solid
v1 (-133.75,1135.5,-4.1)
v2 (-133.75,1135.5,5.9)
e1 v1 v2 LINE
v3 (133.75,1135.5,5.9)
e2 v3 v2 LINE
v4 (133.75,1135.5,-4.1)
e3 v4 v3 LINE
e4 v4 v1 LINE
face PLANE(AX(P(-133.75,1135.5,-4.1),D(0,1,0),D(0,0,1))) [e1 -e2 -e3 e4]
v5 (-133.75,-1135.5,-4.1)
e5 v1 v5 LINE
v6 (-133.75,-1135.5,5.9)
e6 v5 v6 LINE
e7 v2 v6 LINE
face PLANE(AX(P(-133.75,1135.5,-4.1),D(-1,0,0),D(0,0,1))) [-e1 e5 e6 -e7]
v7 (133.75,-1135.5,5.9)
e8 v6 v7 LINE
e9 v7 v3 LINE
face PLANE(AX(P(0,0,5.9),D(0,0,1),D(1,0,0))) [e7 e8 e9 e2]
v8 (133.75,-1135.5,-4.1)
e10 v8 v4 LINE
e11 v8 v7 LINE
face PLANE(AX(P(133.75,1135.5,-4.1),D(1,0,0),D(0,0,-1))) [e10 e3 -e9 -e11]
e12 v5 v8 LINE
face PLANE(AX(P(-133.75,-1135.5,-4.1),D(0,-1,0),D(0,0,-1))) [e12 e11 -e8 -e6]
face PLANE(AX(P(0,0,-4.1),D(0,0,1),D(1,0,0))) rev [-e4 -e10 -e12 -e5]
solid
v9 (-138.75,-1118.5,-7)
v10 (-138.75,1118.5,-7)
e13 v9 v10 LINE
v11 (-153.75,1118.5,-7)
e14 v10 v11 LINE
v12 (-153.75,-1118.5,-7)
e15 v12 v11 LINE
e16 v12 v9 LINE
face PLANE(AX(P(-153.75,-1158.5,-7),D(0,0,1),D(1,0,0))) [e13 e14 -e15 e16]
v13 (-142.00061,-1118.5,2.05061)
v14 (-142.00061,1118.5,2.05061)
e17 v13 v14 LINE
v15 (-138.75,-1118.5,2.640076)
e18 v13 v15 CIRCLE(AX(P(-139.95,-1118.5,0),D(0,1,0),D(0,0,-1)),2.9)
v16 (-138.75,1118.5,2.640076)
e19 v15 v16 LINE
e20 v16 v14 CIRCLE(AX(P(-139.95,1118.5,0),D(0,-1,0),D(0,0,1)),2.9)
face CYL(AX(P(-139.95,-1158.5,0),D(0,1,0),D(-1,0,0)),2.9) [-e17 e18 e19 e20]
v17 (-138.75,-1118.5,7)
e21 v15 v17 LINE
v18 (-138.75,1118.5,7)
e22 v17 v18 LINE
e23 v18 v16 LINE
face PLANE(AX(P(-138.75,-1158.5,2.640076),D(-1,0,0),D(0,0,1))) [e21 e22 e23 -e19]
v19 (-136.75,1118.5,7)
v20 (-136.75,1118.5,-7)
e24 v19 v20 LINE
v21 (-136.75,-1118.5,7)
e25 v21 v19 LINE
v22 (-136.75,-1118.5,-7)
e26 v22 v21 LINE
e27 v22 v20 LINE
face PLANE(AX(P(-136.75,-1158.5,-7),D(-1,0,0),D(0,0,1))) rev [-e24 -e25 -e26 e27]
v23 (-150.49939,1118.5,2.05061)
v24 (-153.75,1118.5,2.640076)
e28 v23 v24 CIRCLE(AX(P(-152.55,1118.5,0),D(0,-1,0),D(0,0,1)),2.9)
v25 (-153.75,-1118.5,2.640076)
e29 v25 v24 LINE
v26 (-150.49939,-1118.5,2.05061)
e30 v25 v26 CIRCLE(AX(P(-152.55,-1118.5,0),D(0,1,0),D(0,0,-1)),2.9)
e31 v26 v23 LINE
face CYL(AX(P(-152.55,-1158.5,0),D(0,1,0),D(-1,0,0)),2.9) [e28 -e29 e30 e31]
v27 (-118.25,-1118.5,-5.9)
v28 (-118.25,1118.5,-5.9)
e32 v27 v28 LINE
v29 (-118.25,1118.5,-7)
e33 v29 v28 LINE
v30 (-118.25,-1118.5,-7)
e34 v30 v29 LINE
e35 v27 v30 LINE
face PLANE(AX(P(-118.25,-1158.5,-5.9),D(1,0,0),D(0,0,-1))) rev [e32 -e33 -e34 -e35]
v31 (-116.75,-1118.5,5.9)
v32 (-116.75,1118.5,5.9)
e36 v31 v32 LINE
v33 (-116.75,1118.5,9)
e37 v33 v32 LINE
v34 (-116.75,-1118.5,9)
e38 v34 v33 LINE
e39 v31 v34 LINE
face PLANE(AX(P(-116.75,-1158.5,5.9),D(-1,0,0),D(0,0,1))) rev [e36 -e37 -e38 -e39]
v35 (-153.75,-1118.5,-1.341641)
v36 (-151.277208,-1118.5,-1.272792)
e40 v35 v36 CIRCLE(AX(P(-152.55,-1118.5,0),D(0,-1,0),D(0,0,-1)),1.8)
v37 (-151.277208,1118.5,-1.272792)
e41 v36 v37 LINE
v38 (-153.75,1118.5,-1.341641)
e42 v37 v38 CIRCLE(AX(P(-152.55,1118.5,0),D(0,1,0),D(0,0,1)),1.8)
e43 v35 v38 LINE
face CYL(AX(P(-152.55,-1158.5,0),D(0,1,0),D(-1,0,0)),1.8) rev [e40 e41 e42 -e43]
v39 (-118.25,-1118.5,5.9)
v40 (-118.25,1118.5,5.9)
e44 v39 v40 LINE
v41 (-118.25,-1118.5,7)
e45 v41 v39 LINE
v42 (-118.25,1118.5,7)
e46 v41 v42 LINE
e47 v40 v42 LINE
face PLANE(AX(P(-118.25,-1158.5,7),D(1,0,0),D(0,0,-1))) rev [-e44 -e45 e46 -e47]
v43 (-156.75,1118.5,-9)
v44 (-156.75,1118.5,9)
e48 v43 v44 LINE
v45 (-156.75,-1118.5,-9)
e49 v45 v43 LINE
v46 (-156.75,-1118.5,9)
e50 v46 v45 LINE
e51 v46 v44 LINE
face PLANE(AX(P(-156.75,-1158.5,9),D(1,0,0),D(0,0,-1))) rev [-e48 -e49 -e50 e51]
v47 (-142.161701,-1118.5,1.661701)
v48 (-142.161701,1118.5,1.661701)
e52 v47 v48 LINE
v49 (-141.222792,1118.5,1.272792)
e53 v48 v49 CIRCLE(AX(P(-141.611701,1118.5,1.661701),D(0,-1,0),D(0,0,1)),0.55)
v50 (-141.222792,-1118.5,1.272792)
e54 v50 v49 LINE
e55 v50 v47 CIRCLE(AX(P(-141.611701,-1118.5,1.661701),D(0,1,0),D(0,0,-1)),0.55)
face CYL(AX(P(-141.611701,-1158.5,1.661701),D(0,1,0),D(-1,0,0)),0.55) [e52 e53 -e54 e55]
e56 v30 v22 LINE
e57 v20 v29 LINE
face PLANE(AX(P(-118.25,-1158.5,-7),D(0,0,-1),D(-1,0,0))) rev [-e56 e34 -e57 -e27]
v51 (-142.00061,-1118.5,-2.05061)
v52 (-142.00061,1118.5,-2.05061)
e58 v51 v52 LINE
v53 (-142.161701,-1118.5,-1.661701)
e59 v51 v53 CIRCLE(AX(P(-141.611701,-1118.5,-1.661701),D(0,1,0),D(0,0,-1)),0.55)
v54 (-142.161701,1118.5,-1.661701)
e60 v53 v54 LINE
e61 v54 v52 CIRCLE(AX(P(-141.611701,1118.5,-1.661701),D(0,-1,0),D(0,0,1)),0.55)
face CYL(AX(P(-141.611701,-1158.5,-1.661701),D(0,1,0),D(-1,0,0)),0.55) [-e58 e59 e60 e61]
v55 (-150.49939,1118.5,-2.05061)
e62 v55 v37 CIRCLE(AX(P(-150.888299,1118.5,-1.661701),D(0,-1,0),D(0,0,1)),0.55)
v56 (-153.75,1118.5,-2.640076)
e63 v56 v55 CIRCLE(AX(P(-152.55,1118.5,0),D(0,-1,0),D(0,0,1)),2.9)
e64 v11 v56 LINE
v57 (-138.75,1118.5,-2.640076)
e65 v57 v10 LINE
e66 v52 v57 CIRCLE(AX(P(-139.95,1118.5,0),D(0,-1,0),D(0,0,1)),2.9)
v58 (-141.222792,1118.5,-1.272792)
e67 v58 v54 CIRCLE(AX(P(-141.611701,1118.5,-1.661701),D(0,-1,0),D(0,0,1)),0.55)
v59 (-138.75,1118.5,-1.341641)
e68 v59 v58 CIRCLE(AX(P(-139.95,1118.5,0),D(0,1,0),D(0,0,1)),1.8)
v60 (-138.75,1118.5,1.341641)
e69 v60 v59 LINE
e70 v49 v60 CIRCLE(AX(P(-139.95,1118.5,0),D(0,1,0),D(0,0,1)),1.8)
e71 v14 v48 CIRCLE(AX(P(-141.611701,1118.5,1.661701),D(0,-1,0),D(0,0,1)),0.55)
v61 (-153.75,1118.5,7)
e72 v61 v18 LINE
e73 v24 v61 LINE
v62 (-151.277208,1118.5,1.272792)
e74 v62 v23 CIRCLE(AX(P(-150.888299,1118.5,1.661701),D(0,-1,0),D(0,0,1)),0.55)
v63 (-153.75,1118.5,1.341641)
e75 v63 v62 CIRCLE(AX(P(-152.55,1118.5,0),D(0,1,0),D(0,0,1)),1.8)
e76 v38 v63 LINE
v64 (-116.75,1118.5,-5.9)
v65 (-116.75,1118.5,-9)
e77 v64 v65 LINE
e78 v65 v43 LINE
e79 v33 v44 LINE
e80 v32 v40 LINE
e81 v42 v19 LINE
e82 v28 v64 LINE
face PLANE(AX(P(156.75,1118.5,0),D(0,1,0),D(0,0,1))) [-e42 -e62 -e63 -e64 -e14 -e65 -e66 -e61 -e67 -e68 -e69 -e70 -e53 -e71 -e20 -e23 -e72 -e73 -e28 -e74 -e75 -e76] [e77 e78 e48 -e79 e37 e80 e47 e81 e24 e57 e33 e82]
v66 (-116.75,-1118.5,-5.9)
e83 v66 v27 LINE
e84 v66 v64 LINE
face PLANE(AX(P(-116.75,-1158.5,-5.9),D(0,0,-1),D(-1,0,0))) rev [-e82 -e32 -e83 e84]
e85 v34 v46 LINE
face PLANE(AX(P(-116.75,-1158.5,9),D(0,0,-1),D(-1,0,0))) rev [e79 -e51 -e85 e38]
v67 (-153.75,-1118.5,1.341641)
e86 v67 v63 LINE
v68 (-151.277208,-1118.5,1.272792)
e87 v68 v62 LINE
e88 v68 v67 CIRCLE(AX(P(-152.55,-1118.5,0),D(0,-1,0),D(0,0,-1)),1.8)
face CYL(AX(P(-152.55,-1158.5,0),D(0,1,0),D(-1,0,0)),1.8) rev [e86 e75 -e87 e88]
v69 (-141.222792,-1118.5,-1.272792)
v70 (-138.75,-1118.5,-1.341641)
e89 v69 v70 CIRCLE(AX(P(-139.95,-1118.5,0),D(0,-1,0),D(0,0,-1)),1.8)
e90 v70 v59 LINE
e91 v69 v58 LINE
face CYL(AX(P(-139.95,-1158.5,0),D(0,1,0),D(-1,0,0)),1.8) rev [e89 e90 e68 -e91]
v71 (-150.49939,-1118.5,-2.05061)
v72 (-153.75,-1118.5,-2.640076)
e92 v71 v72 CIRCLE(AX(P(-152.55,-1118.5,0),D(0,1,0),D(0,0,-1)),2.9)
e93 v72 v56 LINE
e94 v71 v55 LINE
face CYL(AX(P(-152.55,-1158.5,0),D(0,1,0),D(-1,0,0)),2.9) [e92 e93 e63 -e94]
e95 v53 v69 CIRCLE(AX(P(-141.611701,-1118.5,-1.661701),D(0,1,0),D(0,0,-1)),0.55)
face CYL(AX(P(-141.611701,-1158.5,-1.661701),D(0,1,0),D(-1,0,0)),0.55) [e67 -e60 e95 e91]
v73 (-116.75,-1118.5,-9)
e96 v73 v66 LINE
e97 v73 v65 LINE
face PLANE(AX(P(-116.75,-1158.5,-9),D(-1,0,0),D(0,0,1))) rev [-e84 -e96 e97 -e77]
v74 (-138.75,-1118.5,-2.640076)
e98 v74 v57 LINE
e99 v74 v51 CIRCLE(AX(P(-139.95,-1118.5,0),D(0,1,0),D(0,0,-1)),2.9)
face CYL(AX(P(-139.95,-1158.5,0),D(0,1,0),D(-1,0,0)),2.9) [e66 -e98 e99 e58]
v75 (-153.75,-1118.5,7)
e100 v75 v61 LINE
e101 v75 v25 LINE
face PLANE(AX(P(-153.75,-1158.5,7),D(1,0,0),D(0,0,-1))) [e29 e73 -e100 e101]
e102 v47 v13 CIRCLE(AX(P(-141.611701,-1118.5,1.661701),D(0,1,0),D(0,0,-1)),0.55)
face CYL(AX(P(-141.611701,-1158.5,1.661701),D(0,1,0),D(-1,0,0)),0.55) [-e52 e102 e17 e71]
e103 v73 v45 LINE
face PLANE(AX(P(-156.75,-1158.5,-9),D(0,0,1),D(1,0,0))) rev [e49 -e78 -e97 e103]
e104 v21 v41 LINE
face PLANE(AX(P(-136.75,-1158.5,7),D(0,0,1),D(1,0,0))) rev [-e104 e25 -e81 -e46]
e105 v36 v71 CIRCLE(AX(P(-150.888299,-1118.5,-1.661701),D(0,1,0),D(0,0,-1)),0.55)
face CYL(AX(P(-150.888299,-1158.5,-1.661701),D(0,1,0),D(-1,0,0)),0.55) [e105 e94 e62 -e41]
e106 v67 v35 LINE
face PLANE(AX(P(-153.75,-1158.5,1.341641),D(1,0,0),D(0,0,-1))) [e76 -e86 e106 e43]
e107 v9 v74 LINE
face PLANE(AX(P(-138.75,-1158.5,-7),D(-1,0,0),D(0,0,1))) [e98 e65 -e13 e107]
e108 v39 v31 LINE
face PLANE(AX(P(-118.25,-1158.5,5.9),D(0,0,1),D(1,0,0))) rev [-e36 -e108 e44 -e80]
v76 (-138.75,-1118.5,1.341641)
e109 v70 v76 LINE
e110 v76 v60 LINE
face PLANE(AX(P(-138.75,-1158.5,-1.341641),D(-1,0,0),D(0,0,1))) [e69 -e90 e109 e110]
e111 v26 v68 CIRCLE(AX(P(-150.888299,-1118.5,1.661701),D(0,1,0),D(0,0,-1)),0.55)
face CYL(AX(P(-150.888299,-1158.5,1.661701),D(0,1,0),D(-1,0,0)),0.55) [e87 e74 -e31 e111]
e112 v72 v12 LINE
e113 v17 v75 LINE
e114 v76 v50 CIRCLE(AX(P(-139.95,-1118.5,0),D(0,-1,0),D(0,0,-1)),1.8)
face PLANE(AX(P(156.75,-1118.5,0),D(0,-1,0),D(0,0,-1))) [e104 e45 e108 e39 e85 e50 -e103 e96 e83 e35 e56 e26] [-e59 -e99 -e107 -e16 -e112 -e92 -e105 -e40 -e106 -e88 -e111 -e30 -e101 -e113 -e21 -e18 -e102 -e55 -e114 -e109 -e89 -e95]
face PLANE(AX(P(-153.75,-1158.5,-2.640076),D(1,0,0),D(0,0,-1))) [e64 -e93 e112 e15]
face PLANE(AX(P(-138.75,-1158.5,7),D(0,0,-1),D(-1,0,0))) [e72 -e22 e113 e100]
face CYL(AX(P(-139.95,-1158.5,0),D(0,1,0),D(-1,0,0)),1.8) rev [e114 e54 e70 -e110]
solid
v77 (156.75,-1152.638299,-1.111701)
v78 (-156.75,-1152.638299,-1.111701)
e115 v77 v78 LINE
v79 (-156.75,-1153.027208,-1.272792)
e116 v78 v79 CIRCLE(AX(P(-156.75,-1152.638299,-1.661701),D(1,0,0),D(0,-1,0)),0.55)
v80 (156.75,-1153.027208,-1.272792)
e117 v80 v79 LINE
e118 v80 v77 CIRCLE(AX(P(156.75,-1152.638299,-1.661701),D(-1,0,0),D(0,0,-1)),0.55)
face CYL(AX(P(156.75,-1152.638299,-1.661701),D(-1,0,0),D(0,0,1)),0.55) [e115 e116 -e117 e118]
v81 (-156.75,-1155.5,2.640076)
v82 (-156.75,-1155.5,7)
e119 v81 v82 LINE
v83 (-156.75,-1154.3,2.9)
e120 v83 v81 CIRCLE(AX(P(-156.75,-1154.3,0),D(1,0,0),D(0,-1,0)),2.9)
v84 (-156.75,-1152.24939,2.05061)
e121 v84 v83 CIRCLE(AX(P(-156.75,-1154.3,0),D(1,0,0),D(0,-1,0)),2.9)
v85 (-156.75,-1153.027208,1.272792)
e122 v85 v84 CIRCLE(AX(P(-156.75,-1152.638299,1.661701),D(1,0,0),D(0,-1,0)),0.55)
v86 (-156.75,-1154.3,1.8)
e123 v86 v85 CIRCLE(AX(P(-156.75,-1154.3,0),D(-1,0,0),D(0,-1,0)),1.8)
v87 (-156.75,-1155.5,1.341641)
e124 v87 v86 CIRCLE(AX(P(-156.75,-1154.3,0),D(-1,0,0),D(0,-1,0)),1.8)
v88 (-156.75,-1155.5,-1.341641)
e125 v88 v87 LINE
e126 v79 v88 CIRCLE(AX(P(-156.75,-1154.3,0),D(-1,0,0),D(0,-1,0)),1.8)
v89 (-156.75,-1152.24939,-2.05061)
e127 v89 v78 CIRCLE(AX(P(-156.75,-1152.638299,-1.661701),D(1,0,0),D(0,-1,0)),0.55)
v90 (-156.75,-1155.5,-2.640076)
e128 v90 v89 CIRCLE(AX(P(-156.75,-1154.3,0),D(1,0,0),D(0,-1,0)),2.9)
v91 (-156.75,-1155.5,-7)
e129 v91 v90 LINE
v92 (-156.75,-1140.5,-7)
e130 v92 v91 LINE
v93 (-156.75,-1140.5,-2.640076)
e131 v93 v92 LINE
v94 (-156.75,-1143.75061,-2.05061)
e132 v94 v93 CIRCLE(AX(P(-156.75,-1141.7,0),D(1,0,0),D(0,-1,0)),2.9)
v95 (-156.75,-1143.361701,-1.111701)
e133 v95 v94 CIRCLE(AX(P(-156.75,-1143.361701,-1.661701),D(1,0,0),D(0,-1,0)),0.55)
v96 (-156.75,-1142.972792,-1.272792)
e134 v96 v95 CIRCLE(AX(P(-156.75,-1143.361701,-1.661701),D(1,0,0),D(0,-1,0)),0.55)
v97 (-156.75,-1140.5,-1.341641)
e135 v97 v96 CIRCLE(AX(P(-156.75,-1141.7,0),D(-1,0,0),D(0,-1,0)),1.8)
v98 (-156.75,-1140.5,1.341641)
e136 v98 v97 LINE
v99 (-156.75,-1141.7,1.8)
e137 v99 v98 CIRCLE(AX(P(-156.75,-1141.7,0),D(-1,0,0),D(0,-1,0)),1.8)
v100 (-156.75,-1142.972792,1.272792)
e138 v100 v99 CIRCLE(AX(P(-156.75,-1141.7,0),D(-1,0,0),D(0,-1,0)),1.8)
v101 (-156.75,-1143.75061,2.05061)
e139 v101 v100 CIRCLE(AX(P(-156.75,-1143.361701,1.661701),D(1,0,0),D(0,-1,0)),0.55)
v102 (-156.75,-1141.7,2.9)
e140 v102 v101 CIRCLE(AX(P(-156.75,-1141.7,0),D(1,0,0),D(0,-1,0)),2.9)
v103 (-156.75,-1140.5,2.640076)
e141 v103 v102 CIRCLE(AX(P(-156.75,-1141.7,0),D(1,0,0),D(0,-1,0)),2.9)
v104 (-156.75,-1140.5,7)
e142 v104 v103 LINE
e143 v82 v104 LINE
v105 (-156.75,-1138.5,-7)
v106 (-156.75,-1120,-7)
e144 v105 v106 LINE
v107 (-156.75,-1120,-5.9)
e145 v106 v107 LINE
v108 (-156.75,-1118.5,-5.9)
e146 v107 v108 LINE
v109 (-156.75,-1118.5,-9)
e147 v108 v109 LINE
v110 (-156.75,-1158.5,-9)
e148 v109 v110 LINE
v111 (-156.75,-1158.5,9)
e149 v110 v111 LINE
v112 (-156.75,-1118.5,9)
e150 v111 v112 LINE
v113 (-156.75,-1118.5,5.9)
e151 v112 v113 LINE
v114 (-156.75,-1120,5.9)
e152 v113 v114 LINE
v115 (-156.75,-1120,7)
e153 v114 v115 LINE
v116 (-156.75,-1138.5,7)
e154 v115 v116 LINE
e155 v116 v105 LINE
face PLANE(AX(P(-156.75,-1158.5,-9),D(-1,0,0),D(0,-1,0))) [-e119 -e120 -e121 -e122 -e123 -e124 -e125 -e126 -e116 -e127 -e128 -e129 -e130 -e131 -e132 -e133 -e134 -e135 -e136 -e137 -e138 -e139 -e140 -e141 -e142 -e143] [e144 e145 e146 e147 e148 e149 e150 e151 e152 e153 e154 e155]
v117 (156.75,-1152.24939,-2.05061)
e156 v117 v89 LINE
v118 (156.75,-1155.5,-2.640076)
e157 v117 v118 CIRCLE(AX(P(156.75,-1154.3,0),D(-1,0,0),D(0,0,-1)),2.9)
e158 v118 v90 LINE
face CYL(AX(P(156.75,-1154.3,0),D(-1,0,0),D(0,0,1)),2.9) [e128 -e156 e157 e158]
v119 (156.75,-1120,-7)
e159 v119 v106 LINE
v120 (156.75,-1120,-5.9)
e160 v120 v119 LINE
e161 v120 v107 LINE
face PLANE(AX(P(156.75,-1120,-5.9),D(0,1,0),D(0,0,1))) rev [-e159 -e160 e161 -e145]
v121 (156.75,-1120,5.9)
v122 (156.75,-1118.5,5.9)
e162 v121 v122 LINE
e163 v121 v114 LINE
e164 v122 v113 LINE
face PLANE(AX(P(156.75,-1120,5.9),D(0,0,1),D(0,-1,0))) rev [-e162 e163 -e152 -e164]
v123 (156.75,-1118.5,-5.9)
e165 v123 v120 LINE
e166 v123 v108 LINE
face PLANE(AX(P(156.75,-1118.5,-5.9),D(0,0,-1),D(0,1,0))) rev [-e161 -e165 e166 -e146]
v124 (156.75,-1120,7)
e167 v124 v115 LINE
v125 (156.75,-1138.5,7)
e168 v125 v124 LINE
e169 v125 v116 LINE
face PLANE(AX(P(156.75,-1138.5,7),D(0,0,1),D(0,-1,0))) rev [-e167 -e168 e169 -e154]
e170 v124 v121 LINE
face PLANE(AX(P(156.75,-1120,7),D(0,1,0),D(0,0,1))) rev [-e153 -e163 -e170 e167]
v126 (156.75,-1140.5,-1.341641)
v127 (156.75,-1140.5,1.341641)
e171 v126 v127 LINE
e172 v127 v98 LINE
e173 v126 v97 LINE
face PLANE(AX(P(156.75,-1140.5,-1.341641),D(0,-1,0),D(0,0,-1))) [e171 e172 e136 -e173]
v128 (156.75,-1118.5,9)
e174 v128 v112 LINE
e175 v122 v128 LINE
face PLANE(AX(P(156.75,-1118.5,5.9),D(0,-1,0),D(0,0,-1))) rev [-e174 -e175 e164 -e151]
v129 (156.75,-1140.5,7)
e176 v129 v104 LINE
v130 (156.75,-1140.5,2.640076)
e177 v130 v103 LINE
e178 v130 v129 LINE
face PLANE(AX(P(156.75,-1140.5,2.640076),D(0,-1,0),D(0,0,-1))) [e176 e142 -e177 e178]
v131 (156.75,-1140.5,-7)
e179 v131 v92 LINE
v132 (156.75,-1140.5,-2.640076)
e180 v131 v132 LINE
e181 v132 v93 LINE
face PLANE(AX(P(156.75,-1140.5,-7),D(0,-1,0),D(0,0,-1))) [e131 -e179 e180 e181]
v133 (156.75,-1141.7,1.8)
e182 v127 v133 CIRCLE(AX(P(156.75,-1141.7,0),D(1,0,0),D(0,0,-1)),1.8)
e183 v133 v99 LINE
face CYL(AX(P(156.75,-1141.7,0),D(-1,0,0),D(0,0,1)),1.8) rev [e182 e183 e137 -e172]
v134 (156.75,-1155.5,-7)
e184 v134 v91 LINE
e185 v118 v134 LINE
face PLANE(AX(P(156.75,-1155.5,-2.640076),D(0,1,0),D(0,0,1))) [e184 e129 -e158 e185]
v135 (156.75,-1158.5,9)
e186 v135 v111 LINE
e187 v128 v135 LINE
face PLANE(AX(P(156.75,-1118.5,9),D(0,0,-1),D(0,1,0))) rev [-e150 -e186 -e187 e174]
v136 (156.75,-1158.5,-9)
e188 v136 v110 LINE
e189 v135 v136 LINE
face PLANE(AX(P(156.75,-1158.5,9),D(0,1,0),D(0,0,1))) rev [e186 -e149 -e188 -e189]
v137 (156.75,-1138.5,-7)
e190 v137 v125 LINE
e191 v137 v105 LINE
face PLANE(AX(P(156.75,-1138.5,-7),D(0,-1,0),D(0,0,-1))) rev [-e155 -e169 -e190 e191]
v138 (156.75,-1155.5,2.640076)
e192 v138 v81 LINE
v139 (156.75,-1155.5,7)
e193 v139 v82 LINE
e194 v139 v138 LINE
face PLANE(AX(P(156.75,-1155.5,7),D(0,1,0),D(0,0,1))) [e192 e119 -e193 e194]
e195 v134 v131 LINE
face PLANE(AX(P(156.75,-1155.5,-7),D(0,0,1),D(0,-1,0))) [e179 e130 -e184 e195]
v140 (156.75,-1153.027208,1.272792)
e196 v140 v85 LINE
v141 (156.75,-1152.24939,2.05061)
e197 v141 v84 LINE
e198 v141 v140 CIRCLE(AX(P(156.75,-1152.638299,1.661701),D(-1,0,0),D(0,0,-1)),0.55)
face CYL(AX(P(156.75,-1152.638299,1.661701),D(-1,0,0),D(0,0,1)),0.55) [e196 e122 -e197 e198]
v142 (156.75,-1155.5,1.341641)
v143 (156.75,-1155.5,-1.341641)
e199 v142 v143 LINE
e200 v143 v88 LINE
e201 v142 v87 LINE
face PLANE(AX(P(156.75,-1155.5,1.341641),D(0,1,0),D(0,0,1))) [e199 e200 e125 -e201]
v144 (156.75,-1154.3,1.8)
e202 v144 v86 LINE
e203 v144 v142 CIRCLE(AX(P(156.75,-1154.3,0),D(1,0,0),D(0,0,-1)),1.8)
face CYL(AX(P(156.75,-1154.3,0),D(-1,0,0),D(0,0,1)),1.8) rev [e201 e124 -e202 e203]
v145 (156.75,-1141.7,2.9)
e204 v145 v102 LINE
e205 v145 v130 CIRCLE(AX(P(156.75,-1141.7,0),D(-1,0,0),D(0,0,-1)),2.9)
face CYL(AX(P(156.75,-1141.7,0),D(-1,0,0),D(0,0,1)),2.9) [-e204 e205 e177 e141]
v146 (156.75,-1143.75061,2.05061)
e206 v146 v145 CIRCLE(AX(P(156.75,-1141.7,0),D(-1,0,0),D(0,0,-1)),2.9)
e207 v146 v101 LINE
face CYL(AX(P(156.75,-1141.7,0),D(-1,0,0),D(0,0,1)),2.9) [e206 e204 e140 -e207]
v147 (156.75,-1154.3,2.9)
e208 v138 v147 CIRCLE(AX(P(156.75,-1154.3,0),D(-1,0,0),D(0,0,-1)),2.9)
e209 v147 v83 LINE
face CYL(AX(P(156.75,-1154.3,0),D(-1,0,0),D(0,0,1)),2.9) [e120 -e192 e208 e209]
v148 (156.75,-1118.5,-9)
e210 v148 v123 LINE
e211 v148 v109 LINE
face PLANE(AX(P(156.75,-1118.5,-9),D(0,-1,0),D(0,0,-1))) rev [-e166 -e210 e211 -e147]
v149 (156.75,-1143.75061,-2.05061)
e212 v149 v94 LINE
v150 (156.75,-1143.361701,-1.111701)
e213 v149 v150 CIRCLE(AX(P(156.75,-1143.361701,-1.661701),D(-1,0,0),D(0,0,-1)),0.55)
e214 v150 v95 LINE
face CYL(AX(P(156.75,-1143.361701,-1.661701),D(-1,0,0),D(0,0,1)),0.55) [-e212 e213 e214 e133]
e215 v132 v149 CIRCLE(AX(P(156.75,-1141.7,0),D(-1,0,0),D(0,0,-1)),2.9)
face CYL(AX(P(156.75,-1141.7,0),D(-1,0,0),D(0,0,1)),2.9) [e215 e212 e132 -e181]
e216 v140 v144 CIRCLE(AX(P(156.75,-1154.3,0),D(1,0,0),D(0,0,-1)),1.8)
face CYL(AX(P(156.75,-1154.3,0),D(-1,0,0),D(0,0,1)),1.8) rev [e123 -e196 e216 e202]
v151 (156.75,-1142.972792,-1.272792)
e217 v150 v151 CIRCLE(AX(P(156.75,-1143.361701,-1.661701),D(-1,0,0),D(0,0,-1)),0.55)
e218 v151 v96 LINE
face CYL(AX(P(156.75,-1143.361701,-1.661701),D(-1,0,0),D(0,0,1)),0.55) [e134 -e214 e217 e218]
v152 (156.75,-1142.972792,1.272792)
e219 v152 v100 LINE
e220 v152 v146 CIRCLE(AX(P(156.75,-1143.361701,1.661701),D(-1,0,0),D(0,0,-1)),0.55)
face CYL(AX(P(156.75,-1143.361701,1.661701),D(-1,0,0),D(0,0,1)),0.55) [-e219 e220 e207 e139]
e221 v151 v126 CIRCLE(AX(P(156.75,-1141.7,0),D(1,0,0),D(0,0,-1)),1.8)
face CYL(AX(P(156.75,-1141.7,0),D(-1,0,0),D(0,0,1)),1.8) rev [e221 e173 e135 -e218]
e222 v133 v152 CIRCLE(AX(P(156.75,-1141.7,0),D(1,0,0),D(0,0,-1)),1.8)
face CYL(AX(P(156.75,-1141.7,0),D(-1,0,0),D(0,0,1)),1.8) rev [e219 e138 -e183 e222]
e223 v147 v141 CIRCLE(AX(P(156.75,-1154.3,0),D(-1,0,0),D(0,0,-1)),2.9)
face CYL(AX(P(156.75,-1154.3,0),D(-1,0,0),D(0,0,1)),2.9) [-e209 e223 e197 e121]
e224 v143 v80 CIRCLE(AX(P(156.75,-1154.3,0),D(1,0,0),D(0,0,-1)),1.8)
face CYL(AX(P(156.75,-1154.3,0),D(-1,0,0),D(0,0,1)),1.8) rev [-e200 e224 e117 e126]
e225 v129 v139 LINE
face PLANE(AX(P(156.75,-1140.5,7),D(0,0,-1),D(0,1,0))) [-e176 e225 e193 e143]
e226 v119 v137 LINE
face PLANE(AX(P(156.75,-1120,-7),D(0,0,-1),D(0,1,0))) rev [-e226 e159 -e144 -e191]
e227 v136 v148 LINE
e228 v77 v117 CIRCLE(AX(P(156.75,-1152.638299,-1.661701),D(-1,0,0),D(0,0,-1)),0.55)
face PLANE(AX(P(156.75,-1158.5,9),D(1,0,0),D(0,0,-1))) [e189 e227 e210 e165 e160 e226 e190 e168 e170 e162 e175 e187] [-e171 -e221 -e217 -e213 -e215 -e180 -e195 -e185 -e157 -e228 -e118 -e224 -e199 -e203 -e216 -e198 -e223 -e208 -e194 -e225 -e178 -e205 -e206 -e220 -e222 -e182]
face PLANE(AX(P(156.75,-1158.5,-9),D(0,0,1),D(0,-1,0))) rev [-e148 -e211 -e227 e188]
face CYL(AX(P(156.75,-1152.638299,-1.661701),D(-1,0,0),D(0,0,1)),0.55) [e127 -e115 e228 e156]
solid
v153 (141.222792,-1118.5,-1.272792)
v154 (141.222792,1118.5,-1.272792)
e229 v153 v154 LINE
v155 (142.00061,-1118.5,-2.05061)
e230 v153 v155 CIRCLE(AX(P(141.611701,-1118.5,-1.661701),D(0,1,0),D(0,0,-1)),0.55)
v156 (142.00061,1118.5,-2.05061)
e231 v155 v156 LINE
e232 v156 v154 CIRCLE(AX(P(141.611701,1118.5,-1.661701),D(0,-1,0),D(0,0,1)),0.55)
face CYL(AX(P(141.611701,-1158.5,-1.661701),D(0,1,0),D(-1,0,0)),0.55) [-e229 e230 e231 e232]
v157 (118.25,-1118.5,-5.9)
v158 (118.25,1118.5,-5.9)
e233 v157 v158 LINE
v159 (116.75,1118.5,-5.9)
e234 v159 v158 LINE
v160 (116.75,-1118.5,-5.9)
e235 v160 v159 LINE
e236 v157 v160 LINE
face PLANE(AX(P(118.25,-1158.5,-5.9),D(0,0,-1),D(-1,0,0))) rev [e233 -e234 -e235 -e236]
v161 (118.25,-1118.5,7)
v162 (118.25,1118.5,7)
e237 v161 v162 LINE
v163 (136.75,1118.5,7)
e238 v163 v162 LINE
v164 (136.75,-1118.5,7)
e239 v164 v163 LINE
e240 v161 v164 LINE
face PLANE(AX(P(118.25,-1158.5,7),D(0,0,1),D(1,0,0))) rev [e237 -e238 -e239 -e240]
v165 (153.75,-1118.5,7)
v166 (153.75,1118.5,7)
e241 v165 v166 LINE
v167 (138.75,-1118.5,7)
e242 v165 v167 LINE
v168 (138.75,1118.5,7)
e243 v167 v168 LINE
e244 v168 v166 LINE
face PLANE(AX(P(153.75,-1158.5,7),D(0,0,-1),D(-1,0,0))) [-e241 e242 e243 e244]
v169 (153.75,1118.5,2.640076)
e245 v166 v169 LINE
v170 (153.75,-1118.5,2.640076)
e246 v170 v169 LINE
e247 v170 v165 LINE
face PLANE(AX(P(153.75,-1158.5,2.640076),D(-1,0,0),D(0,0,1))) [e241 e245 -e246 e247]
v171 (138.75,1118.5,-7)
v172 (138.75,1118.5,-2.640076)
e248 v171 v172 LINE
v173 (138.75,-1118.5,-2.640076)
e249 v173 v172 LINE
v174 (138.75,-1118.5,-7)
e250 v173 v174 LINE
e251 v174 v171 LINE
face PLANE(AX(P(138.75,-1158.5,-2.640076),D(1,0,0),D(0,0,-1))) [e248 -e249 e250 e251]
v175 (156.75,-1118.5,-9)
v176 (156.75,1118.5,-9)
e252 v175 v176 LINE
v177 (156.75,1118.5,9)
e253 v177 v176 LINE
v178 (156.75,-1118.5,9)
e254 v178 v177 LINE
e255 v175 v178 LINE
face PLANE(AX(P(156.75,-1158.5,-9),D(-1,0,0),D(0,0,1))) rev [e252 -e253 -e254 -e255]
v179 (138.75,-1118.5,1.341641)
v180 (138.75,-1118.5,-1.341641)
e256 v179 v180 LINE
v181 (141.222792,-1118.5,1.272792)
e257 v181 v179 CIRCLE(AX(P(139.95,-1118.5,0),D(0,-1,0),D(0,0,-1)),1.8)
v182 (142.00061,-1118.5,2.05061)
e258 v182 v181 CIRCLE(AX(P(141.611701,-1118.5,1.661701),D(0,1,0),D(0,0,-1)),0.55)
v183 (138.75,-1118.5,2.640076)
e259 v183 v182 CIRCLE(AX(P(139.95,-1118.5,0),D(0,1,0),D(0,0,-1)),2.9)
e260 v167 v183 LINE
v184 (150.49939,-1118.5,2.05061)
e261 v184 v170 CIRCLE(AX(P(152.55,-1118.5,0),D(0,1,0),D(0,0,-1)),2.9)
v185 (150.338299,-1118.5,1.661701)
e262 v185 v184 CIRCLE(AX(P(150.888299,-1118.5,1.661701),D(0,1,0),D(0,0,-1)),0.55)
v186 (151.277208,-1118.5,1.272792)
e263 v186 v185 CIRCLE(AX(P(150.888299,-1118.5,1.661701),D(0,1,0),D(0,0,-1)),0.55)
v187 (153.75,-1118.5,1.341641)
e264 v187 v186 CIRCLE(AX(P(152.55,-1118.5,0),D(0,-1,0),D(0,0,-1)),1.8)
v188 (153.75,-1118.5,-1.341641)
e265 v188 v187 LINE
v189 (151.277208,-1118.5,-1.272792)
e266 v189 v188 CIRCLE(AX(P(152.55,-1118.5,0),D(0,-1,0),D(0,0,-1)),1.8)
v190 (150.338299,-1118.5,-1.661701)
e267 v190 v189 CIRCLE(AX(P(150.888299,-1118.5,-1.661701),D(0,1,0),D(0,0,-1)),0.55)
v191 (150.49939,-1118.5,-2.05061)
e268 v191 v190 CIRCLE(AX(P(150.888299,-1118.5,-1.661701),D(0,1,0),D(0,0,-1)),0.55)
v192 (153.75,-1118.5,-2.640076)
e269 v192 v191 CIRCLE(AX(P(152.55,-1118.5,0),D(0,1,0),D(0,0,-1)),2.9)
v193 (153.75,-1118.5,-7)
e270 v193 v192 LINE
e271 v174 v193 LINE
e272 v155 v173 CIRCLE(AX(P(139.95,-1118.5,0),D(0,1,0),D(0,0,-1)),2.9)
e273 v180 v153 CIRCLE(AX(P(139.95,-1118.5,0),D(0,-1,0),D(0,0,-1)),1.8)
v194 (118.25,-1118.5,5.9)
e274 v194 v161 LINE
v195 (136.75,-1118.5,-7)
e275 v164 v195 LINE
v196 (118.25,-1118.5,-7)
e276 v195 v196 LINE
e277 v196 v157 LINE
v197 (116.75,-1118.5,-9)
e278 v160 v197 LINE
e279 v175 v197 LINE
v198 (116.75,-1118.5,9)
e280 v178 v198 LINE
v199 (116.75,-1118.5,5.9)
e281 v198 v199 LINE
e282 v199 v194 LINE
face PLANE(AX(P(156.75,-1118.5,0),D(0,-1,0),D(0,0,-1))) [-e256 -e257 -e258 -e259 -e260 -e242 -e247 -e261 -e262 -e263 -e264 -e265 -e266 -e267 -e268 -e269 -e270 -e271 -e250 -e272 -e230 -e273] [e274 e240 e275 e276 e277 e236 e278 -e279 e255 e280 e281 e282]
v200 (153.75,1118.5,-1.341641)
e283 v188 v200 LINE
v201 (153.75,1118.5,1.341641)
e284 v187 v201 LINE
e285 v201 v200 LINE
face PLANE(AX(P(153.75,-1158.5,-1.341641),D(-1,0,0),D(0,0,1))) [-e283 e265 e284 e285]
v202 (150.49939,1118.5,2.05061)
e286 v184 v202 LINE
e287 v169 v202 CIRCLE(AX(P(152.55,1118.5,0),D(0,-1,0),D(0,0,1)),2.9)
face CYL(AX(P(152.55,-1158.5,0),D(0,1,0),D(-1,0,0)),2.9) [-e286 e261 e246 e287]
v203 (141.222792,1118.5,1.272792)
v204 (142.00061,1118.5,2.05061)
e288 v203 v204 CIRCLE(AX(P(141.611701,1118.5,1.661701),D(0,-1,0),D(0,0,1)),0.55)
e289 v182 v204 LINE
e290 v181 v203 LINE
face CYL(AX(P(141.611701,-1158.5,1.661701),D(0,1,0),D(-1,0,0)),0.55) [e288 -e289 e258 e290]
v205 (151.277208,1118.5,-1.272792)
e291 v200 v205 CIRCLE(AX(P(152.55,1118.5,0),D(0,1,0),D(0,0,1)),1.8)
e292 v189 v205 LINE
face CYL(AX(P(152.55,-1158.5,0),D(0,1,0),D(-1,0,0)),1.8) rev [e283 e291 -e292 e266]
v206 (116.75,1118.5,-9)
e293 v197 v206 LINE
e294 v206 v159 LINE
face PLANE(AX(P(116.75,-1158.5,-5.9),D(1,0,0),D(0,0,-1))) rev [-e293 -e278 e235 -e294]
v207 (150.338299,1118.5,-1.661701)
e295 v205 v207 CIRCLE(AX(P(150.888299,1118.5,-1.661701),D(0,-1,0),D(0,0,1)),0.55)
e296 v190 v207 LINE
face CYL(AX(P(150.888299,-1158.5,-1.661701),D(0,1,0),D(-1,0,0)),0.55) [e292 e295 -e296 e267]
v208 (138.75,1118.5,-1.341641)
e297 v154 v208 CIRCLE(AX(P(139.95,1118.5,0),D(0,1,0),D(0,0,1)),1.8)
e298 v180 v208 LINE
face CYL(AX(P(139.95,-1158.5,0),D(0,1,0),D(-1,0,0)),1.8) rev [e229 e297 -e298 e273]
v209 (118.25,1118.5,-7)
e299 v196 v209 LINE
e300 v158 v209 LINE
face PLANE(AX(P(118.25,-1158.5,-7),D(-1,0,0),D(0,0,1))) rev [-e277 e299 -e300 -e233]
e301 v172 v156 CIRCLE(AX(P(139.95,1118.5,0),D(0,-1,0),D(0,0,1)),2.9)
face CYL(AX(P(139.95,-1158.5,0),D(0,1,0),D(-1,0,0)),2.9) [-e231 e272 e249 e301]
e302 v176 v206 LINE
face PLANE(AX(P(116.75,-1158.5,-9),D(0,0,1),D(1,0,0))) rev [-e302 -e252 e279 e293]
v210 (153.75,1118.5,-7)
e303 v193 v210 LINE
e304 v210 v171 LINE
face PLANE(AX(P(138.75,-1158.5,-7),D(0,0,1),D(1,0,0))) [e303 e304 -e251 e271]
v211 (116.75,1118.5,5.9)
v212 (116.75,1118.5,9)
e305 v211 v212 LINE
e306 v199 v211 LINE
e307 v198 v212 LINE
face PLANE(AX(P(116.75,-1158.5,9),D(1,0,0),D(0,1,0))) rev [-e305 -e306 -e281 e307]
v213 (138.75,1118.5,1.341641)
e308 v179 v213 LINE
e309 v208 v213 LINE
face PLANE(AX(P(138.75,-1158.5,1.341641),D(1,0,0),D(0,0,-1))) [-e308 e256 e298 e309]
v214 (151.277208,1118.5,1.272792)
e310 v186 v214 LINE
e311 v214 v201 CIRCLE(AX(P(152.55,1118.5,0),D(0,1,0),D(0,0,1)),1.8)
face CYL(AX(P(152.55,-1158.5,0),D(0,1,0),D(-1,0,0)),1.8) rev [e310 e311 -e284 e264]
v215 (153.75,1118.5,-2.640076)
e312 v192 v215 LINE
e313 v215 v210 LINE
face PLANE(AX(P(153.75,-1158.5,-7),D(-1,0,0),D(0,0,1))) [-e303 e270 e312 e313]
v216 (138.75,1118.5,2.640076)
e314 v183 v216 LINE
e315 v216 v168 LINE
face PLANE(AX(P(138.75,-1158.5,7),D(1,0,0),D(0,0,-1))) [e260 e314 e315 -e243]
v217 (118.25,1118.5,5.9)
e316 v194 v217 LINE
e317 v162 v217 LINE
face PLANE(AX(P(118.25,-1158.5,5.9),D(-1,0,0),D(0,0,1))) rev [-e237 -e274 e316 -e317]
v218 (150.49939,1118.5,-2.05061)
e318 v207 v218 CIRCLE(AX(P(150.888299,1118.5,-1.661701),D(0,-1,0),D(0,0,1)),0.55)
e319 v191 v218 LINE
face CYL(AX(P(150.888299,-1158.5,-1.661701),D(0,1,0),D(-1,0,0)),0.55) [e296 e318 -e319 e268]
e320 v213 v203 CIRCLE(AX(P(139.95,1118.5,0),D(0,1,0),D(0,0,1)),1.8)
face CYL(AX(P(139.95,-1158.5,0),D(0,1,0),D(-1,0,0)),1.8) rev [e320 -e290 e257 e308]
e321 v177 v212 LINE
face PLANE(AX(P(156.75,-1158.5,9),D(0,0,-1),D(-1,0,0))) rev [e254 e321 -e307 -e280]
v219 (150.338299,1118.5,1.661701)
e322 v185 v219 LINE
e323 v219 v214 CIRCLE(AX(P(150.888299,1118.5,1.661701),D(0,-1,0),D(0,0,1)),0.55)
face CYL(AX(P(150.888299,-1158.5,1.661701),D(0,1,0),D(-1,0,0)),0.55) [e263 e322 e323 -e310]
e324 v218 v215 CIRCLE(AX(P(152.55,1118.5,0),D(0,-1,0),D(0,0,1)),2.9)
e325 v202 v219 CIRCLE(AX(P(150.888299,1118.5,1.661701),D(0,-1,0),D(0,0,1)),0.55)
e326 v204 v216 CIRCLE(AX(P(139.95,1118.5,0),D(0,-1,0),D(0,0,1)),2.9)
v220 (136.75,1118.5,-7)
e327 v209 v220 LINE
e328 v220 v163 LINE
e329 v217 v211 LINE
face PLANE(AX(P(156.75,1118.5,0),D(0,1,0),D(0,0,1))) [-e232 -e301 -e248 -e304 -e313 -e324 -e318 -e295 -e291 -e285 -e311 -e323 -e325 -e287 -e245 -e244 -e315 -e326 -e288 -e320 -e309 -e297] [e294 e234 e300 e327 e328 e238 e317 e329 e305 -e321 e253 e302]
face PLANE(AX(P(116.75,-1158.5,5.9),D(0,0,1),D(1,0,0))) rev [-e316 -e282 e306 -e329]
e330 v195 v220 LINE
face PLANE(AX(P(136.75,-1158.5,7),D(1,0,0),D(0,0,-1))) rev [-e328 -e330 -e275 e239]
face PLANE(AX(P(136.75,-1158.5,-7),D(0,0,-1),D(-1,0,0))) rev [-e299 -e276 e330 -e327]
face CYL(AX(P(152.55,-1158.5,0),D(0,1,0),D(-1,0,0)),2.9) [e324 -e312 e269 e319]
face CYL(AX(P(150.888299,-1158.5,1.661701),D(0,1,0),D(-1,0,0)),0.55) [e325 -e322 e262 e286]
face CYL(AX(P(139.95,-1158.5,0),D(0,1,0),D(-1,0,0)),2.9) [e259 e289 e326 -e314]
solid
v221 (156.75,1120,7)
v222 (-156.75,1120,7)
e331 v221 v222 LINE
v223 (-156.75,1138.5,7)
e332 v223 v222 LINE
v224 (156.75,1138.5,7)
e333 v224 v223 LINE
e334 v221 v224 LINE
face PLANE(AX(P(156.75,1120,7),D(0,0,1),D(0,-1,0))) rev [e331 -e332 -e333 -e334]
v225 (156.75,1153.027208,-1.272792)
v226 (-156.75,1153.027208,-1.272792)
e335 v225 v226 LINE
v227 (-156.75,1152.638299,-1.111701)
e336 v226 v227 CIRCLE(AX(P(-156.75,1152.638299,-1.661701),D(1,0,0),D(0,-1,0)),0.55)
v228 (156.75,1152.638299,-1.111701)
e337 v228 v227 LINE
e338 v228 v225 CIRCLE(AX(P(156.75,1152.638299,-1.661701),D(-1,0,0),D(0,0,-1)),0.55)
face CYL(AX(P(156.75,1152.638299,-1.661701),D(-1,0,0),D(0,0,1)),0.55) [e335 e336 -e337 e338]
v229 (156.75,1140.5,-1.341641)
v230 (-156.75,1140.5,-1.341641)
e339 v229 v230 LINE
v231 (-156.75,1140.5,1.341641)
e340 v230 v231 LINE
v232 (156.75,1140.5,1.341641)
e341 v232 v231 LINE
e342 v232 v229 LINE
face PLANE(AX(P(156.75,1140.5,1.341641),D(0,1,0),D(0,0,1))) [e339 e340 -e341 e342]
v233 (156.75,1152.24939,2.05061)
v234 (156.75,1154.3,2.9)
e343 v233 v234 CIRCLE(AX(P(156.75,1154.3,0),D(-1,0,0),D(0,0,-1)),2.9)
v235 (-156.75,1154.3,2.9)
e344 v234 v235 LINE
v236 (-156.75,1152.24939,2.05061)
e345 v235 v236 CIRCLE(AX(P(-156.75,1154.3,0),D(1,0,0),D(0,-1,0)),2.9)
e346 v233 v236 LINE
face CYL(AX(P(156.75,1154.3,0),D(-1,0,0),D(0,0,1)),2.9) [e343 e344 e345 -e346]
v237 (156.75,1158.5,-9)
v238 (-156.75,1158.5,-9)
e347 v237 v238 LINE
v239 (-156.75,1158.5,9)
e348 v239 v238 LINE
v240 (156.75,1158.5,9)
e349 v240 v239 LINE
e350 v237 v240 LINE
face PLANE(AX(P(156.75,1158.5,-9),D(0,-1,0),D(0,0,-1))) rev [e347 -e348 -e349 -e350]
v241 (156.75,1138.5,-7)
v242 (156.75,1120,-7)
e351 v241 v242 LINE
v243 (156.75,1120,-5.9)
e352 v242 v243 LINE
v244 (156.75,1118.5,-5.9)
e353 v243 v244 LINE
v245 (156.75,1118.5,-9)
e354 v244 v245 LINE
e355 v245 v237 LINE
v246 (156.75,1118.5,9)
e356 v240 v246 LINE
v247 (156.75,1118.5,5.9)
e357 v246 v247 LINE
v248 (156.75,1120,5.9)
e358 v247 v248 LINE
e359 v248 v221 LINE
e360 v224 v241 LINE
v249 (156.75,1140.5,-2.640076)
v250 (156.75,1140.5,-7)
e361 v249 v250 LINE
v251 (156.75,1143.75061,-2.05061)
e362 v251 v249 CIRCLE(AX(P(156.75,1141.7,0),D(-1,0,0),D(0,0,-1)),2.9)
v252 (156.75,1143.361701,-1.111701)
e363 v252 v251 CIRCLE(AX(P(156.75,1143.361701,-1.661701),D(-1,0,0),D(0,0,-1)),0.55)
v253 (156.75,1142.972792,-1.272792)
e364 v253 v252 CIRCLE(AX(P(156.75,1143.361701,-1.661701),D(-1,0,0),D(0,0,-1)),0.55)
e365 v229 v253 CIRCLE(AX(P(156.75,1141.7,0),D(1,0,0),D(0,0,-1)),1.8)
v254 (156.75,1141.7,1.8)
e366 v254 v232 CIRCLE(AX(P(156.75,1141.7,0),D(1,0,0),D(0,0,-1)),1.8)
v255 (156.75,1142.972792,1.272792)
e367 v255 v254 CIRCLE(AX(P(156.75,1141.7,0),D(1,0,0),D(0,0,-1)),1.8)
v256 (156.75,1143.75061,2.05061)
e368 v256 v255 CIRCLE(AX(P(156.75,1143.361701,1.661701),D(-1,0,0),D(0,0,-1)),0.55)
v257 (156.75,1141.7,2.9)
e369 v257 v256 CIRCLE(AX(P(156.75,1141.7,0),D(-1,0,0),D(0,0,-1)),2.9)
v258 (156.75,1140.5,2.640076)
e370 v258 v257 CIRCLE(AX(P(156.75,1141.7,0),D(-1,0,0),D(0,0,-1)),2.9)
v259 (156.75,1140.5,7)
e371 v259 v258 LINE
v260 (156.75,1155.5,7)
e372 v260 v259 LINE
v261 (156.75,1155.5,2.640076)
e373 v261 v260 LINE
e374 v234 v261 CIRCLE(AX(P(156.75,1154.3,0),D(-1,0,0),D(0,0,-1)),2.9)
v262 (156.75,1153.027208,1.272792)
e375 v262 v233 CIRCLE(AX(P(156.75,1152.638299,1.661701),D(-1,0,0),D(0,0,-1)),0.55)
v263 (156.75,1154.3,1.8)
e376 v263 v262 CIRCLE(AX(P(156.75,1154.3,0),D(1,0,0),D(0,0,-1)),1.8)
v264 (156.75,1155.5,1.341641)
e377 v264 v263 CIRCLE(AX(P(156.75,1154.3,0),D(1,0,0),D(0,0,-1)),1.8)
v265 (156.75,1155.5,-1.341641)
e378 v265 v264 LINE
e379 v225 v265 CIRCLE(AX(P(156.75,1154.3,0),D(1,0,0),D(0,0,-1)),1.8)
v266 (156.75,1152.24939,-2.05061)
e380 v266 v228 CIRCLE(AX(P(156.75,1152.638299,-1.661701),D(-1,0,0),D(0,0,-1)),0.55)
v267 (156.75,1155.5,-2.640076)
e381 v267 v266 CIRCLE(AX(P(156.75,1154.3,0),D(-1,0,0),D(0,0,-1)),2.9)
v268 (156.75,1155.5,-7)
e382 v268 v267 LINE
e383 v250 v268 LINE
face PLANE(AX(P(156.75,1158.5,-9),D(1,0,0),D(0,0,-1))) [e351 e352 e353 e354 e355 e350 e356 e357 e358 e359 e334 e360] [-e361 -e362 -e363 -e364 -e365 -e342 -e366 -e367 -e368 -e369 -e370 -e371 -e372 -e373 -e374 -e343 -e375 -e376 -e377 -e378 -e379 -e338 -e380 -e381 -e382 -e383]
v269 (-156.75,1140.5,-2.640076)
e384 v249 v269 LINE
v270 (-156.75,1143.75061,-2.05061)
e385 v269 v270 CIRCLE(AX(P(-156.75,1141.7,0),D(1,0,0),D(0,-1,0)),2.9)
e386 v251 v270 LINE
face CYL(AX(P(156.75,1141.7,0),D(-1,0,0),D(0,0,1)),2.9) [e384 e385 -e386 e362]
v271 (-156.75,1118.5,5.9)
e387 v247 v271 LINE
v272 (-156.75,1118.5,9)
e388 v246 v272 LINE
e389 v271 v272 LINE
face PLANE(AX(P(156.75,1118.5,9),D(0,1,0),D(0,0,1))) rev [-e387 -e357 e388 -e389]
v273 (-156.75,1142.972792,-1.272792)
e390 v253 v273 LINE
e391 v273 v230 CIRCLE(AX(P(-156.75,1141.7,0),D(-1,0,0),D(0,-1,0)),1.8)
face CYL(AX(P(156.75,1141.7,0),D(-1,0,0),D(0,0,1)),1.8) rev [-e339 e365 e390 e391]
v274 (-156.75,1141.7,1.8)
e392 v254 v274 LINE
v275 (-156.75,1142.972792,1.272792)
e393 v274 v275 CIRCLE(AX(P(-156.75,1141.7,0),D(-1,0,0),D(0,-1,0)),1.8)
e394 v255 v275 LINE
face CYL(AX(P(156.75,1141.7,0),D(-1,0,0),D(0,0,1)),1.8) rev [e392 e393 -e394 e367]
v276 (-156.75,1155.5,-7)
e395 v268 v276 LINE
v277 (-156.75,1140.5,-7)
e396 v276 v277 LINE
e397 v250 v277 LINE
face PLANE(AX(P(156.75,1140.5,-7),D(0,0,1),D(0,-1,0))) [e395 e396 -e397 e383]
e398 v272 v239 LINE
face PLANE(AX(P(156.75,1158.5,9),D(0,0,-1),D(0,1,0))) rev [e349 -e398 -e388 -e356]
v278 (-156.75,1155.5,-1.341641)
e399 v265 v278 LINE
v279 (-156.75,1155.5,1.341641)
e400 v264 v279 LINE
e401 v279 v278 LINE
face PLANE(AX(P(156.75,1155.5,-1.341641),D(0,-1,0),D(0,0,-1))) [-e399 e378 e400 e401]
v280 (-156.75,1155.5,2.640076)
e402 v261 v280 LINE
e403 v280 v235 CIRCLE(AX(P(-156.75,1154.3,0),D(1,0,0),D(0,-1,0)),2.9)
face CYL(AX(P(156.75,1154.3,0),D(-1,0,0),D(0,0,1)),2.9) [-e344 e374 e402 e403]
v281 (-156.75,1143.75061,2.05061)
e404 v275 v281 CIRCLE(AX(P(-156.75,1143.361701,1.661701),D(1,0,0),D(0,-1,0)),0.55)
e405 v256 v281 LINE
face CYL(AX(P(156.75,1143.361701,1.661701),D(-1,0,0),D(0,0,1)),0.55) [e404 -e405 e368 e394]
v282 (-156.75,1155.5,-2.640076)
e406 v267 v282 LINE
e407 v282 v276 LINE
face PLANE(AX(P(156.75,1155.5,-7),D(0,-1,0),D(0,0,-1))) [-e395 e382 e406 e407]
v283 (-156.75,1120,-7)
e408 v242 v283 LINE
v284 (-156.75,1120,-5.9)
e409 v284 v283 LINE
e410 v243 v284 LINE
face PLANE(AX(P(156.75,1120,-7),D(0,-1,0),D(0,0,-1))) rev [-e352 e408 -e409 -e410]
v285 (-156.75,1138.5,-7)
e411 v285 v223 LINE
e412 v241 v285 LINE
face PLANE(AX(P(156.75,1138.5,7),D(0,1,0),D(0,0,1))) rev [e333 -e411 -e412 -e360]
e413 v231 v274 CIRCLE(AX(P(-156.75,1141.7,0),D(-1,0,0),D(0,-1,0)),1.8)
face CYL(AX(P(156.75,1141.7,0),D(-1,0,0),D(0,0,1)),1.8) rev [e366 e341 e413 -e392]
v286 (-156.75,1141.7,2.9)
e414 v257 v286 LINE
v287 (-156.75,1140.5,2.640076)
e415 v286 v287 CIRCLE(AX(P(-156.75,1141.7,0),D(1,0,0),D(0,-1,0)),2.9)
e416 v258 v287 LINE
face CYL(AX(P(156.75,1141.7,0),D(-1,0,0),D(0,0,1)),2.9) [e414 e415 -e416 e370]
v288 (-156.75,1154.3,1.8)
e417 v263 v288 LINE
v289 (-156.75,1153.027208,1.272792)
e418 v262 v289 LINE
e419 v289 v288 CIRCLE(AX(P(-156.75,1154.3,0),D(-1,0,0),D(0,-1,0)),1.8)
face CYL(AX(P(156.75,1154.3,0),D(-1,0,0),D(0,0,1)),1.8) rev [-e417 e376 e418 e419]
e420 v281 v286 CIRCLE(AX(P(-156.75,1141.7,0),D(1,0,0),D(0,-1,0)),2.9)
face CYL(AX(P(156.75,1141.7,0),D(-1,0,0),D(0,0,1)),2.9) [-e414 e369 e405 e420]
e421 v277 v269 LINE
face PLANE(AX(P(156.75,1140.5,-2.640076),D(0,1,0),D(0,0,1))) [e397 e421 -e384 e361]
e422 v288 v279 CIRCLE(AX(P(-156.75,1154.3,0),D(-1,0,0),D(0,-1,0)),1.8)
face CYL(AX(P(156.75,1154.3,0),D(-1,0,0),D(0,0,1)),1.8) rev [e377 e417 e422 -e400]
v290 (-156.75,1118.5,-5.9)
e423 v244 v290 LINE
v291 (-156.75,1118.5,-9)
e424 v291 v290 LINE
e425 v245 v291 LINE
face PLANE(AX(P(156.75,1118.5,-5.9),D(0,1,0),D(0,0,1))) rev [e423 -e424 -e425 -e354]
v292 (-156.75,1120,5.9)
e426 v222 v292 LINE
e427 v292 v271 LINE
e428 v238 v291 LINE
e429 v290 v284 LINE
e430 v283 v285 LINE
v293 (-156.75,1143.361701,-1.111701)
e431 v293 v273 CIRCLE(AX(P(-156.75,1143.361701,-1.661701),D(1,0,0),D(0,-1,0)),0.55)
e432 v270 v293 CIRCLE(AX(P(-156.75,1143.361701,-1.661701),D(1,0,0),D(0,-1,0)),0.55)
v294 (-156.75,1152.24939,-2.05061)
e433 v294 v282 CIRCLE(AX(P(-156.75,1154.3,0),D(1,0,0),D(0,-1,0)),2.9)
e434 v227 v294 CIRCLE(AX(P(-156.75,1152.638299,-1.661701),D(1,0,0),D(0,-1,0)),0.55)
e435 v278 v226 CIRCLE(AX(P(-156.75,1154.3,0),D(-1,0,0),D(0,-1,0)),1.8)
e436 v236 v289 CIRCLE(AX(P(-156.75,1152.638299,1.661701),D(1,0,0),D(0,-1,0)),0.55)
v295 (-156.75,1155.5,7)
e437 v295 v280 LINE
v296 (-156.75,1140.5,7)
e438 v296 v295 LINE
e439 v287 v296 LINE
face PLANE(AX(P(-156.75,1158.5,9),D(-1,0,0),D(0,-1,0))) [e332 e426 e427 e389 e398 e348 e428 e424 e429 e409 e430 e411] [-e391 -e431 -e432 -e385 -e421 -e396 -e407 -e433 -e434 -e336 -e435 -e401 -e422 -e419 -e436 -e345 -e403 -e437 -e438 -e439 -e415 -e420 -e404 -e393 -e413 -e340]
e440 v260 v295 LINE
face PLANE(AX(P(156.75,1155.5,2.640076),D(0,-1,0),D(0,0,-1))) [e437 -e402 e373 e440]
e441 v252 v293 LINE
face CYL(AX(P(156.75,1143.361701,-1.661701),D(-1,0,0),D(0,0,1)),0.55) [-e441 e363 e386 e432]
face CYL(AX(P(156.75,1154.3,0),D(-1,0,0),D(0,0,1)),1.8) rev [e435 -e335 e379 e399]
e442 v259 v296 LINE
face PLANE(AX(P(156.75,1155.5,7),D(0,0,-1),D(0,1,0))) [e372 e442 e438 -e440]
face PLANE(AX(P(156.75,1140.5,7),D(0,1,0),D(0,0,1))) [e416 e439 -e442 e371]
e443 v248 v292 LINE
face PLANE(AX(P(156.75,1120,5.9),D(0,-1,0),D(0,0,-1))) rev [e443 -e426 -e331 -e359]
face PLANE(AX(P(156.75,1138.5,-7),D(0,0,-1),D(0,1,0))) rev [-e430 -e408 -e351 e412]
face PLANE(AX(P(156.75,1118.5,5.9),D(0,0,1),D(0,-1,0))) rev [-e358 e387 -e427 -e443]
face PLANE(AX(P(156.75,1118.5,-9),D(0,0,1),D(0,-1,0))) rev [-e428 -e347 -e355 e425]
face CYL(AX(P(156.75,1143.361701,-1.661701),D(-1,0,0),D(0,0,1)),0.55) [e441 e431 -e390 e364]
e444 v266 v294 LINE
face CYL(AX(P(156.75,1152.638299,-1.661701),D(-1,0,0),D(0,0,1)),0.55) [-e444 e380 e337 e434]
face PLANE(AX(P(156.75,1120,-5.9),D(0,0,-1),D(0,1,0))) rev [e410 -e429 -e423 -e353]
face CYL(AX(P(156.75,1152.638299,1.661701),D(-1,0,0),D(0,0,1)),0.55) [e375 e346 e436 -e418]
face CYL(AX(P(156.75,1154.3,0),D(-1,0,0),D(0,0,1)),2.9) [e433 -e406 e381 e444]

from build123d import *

# Parameters (mm, degrees)
MEMBER_1_DEPTH   = 313.5
MEMBER_1_2_DEPTH = 313.5
MEMBER_1_3_DEPTH = 2319
MEMBER_1_4_DEPTH = 2319
EXTRUDE_START    = -3.1
SKETCH_2_W       = 267.5
SKETCH_2_H       = 2271
EXTRUDE_1_DEPTH  = 10


with BuildPart() as part:
    # Sketch1 → Member 1 (new body)
    with BuildSketch(Plane(origin=(-156.75, 1158.5, 0), x_dir=(0, 0, -1), z_dir=(1, 0, 0))):
        Polygon((7, -38.5), (5.9, -38.5), (5.9, -40), (7, -40), (9, -40), (9, 0), (-9, 0), (-9, -40), (-7, -40), (-5.9, -40), (-5.9, -38.5), (-7, -38.5), (-7, -20), (7, -20), align=None)
        with BuildLine():
            Line((-1.341640786, -18), (1.341640786, -18))
            ThreePointArc((1.341640786, -18), (1.799302724, -16.749903013), (1.272792206, -15.527207794))
            ThreePointArc((1.272792206, -15.527207794), (1.272792206, -14.749390335), (2.050609665, -14.749390335))
            ThreePointArc((2.050609665, -14.749390335), (2.853462499, -16.282552641), (2.640075756, -18))
            Line((2.640075756, -18), (7, -18))
            Line((7, -18), (7, -3))
            Line((7, -3), (2.640075756, -3))
            ThreePointArc((2.640075756, -3), (2.853462499, -4.717447359), (2.050609665, -6.250609665))
            ThreePointArc((2.050609665, -6.250609665), (1.272792206, -6.250609665), (1.272792206, -5.472792206))
            ThreePointArc((1.272792206, -5.472792206), (1.799302724, -4.250096987), (1.341640786, -3))
            Line((1.341640786, -3), (-1.341640786, -3))
            ThreePointArc((-1.341640786, -3), (-1.799302724, -4.250096987), (-1.272792206, -5.472792206))
            ThreePointArc((-1.272792206, -5.472792206), (-1.272792206, -6.250609665), (-2.050609665, -6.250609665))
            ThreePointArc((-2.050609665, -6.250609665), (-2.853462499, -4.717447359), (-2.640075756, -3))
            Line((-2.640075756, -3), (-7, -3))
            Line((-7, -3), (-7, -18))
            Line((-7, -18), (-2.640075756, -18))
            ThreePointArc((-2.640075756, -18), (-2.853462499, -16.282552641), (-2.050609665, -14.749390335))
            ThreePointArc((-2.050609665, -14.749390335), (-1.272792206, -14.749390335), (-1.272792206, -15.527207794))
            ThreePointArc((-1.272792206, -15.527207794), (-1.799302724, -16.749903013), (-1.341640786, -18))
        make_face(mode=Mode.SUBTRACT)
    extrude(amount=MEMBER_1_DEPTH)


with BuildPart() as body_2:
    # Sketch1 on segment 2 (carried to segment 2) → Member 1 2 (new body)
    with BuildSketch(Plane(origin=(-156.75, -1158.5, 0), x_dir=(0, 0, 1), z_dir=(1, 0, 0))):
        Polygon((7, -38.5), (5.9, -38.5), (5.9, -40), (7, -40), (9, -40), (9, 0), (-9, 0), (-9, -40), (-7, -40), (-5.9, -40), (-5.9, -38.5), (-7, -38.5), (-7, -20), (7, -20), align=None)
        with BuildLine():
            Line((-1.341640786, -18), (1.341640786, -18))
            ThreePointArc((1.341640786, -18), (1.799302724, -16.749903013), (1.272792206, -15.527207794))
            ThreePointArc((1.272792206, -15.527207794), (1.272792206, -14.749390335), (2.050609665, -14.749390335))
            ThreePointArc((2.050609665, -14.749390335), (2.853462499, -16.282552641), (2.640075756, -18))
            Line((2.640075756, -18), (7, -18))
            Line((7, -18), (7, -3))
            Line((7, -3), (2.640075756, -3))
            ThreePointArc((2.640075756, -3), (2.853462499, -4.717447359), (2.050609665, -6.250609665))
            ThreePointArc((2.050609665, -6.250609665), (1.272792206, -6.250609665), (1.272792206, -5.472792206))
            ThreePointArc((1.272792206, -5.472792206), (1.799302724, -4.250096987), (1.341640786, -3))
            Line((1.341640786, -3), (-1.341640786, -3))
            ThreePointArc((-1.341640786, -3), (-1.799302724, -4.250096987), (-1.272792206, -5.472792206))
            ThreePointArc((-1.272792206, -5.472792206), (-1.272792206, -6.250609665), (-2.050609665, -6.250609665))
            ThreePointArc((-2.050609665, -6.250609665), (-2.853462499, -4.717447359), (-2.640075756, -3))
            Line((-2.640075756, -3), (-7, -3))
            Line((-7, -3), (-7, -18))
            Line((-7, -18), (-2.640075756, -18))
            ThreePointArc((-2.640075756, -18), (-2.853462499, -16.282552641), (-2.050609665, -14.749390335))
            ThreePointArc((-2.050609665, -14.749390335), (-1.272792206, -14.749390335), (-1.272792206, -15.527207794))
            ThreePointArc((-1.272792206, -15.527207794), (-1.799302724, -16.749903013), (-1.341640786, -18))
        make_face(mode=Mode.SUBTRACT)
    extrude(amount=MEMBER_1_2_DEPTH)


with BuildPart() as body_3:
    # Sketch1 on segment 3 (carried to segment 3) → Member 1 3 (new body)
    with BuildSketch(Plane(origin=(-156.75, 1159.5, 0), x_dir=(0, 0, 1), z_dir=(0, -1, 0))):
        Polygon((7, -38.5), (5.9, -38.5), (5.9, -40), (7, -40), (9, -40), (9, 0), (-9, 0), (-9, -40), (-7, -40), (-5.9, -40), (-5.9, -38.5), (-7, -38.5), (-7, -20), (7, -20), align=None)
        with BuildLine():
            Line((-1.341640786, -18), (1.341640786, -18))
            ThreePointArc((1.341640786, -18), (1.799302724, -16.749903013), (1.272792206, -15.527207794))
            ThreePointArc((1.272792206, -15.527207794), (1.272792206, -14.749390335), (2.050609665, -14.749390335))
            ThreePointArc((2.050609665, -14.749390335), (2.853462499, -16.282552641), (2.640075756, -18))
            Line((2.640075756, -18), (7, -18))
            Line((7, -18), (7, -3))
            Line((7, -3), (2.640075756, -3))
            ThreePointArc((2.640075756, -3), (2.853462499, -4.717447359), (2.050609665, -6.250609665))
            ThreePointArc((2.050609665, -6.250609665), (1.272792206, -6.250609665), (1.272792206, -5.472792206))
            ThreePointArc((1.272792206, -5.472792206), (1.799302724, -4.250096987), (1.341640786, -3))
            Line((1.341640786, -3), (-1.341640786, -3))
            ThreePointArc((-1.341640786, -3), (-1.799302724, -4.250096987), (-1.272792206, -5.472792206))
            ThreePointArc((-1.272792206, -5.472792206), (-1.272792206, -6.250609665), (-2.050609665, -6.250609665))
            ThreePointArc((-2.050609665, -6.250609665), (-2.853462499, -4.717447359), (-2.640075756, -3))
            Line((-2.640075756, -3), (-7, -3))
            Line((-7, -3), (-7, -18))
            Line((-7, -18), (-2.640075756, -18))
            ThreePointArc((-2.640075756, -18), (-2.853462499, -16.282552641), (-2.050609665, -14.749390335))
            ThreePointArc((-2.050609665, -14.749390335), (-1.272792206, -14.749390335), (-1.272792206, -15.527207794))
            ThreePointArc((-1.272792206, -15.527207794), (-1.799302724, -16.749903013), (-1.341640786, -18))
        make_face(mode=Mode.SUBTRACT)
    extrude(amount=MEMBER_1_3_DEPTH)

    # Member 1 3 end butt 1
    split(bisect_by=Plane(origin=(-156.75, 1118.5, 0), x_dir=(1, 0, 0), z_dir=(0, -1, 0)), keep=Keep.TOP)

    # Member 1 3 end butt 2
    split(bisect_by=Plane(origin=(-156.75, -1118.5, 0), x_dir=(-1, 0, 0), z_dir=(0, 1, 0)), keep=Keep.TOP)


with BuildPart() as body_4:
    # Sketch1 on segment 4 (carried to segment 4) → Member 1 4 (new body)
    with BuildSketch(Plane(origin=(156.75, 1159.5, 0), x_dir=(0, 0, -1), z_dir=(0, -1, 0))):
        Polygon((7, -38.5), (5.9, -38.5), (5.9, -40), (7, -40), (9, -40), (9, 0), (-9, 0), (-9, -40), (-7, -40), (-5.9, -40), (-5.9, -38.5), (-7, -38.5), (-7, -20), (7, -20), align=None)
        with BuildLine():
            Line((-1.341640786, -18), (1.341640786, -18))
            ThreePointArc((1.341640786, -18), (1.799302724, -16.749903013), (1.272792206, -15.527207794))
            ThreePointArc((1.272792206, -15.527207794), (1.272792206, -14.749390335), (2.050609665, -14.749390335))
            ThreePointArc((2.050609665, -14.749390335), (2.853462499, -16.282552641), (2.640075756, -18))
            Line((2.640075756, -18), (7, -18))
            Line((7, -18), (7, -3))
            Line((7, -3), (2.640075756, -3))
            ThreePointArc((2.640075756, -3), (2.853462499, -4.717447359), (2.050609665, -6.250609665))
            ThreePointArc((2.050609665, -6.250609665), (1.272792206, -6.250609665), (1.272792206, -5.472792206))
            ThreePointArc((1.272792206, -5.472792206), (1.799302724, -4.250096987), (1.341640786, -3))
            Line((1.341640786, -3), (-1.341640786, -3))
            ThreePointArc((-1.341640786, -3), (-1.799302724, -4.250096987), (-1.272792206, -5.472792206))
            ThreePointArc((-1.272792206, -5.472792206), (-1.272792206, -6.250609665), (-2.050609665, -6.250609665))
            ThreePointArc((-2.050609665, -6.250609665), (-2.853462499, -4.717447359), (-2.640075756, -3))
            Line((-2.640075756, -3), (-7, -3))
            Line((-7, -3), (-7, -18))
            Line((-7, -18), (-2.640075756, -18))
            ThreePointArc((-2.640075756, -18), (-2.853462499, -16.282552641), (-2.050609665, -14.749390335))
            ThreePointArc((-2.050609665, -14.749390335), (-1.272792206, -14.749390335), (-1.272792206, -15.527207794))
            ThreePointArc((-1.272792206, -15.527207794), (-1.799302724, -16.749903013), (-1.341640786, -18))
        make_face(mode=Mode.SUBTRACT)
    extrude(amount=MEMBER_1_4_DEPTH)

    # Member 1 4 end butt 1
    split(bisect_by=Plane(origin=(156.75, 1118.5, 0), x_dir=(1, 0, 0), z_dir=(0, -1, 0)), keep=Keep.TOP)

    # Member 1 4 end butt 2
    split(bisect_by=Plane(origin=(156.75, -1118.5, 0), x_dir=(-1, 0, 0), z_dir=(0, 1, 0)), keep=Keep.TOP)


with BuildPart() as body_5:
    # 草图2 → 凸台-拉伸1 (new body)
    with BuildSketch(Plane.XY.offset(9).offset(EXTRUDE_START)):
        Rectangle(SKETCH_2_W, SKETCH_2_H)
    extrude(amount=-EXTRUDE_1_DEPTH)


solid = Compound([part.part, body_2.part, body_3.part, body_4.part, body_5.part])
